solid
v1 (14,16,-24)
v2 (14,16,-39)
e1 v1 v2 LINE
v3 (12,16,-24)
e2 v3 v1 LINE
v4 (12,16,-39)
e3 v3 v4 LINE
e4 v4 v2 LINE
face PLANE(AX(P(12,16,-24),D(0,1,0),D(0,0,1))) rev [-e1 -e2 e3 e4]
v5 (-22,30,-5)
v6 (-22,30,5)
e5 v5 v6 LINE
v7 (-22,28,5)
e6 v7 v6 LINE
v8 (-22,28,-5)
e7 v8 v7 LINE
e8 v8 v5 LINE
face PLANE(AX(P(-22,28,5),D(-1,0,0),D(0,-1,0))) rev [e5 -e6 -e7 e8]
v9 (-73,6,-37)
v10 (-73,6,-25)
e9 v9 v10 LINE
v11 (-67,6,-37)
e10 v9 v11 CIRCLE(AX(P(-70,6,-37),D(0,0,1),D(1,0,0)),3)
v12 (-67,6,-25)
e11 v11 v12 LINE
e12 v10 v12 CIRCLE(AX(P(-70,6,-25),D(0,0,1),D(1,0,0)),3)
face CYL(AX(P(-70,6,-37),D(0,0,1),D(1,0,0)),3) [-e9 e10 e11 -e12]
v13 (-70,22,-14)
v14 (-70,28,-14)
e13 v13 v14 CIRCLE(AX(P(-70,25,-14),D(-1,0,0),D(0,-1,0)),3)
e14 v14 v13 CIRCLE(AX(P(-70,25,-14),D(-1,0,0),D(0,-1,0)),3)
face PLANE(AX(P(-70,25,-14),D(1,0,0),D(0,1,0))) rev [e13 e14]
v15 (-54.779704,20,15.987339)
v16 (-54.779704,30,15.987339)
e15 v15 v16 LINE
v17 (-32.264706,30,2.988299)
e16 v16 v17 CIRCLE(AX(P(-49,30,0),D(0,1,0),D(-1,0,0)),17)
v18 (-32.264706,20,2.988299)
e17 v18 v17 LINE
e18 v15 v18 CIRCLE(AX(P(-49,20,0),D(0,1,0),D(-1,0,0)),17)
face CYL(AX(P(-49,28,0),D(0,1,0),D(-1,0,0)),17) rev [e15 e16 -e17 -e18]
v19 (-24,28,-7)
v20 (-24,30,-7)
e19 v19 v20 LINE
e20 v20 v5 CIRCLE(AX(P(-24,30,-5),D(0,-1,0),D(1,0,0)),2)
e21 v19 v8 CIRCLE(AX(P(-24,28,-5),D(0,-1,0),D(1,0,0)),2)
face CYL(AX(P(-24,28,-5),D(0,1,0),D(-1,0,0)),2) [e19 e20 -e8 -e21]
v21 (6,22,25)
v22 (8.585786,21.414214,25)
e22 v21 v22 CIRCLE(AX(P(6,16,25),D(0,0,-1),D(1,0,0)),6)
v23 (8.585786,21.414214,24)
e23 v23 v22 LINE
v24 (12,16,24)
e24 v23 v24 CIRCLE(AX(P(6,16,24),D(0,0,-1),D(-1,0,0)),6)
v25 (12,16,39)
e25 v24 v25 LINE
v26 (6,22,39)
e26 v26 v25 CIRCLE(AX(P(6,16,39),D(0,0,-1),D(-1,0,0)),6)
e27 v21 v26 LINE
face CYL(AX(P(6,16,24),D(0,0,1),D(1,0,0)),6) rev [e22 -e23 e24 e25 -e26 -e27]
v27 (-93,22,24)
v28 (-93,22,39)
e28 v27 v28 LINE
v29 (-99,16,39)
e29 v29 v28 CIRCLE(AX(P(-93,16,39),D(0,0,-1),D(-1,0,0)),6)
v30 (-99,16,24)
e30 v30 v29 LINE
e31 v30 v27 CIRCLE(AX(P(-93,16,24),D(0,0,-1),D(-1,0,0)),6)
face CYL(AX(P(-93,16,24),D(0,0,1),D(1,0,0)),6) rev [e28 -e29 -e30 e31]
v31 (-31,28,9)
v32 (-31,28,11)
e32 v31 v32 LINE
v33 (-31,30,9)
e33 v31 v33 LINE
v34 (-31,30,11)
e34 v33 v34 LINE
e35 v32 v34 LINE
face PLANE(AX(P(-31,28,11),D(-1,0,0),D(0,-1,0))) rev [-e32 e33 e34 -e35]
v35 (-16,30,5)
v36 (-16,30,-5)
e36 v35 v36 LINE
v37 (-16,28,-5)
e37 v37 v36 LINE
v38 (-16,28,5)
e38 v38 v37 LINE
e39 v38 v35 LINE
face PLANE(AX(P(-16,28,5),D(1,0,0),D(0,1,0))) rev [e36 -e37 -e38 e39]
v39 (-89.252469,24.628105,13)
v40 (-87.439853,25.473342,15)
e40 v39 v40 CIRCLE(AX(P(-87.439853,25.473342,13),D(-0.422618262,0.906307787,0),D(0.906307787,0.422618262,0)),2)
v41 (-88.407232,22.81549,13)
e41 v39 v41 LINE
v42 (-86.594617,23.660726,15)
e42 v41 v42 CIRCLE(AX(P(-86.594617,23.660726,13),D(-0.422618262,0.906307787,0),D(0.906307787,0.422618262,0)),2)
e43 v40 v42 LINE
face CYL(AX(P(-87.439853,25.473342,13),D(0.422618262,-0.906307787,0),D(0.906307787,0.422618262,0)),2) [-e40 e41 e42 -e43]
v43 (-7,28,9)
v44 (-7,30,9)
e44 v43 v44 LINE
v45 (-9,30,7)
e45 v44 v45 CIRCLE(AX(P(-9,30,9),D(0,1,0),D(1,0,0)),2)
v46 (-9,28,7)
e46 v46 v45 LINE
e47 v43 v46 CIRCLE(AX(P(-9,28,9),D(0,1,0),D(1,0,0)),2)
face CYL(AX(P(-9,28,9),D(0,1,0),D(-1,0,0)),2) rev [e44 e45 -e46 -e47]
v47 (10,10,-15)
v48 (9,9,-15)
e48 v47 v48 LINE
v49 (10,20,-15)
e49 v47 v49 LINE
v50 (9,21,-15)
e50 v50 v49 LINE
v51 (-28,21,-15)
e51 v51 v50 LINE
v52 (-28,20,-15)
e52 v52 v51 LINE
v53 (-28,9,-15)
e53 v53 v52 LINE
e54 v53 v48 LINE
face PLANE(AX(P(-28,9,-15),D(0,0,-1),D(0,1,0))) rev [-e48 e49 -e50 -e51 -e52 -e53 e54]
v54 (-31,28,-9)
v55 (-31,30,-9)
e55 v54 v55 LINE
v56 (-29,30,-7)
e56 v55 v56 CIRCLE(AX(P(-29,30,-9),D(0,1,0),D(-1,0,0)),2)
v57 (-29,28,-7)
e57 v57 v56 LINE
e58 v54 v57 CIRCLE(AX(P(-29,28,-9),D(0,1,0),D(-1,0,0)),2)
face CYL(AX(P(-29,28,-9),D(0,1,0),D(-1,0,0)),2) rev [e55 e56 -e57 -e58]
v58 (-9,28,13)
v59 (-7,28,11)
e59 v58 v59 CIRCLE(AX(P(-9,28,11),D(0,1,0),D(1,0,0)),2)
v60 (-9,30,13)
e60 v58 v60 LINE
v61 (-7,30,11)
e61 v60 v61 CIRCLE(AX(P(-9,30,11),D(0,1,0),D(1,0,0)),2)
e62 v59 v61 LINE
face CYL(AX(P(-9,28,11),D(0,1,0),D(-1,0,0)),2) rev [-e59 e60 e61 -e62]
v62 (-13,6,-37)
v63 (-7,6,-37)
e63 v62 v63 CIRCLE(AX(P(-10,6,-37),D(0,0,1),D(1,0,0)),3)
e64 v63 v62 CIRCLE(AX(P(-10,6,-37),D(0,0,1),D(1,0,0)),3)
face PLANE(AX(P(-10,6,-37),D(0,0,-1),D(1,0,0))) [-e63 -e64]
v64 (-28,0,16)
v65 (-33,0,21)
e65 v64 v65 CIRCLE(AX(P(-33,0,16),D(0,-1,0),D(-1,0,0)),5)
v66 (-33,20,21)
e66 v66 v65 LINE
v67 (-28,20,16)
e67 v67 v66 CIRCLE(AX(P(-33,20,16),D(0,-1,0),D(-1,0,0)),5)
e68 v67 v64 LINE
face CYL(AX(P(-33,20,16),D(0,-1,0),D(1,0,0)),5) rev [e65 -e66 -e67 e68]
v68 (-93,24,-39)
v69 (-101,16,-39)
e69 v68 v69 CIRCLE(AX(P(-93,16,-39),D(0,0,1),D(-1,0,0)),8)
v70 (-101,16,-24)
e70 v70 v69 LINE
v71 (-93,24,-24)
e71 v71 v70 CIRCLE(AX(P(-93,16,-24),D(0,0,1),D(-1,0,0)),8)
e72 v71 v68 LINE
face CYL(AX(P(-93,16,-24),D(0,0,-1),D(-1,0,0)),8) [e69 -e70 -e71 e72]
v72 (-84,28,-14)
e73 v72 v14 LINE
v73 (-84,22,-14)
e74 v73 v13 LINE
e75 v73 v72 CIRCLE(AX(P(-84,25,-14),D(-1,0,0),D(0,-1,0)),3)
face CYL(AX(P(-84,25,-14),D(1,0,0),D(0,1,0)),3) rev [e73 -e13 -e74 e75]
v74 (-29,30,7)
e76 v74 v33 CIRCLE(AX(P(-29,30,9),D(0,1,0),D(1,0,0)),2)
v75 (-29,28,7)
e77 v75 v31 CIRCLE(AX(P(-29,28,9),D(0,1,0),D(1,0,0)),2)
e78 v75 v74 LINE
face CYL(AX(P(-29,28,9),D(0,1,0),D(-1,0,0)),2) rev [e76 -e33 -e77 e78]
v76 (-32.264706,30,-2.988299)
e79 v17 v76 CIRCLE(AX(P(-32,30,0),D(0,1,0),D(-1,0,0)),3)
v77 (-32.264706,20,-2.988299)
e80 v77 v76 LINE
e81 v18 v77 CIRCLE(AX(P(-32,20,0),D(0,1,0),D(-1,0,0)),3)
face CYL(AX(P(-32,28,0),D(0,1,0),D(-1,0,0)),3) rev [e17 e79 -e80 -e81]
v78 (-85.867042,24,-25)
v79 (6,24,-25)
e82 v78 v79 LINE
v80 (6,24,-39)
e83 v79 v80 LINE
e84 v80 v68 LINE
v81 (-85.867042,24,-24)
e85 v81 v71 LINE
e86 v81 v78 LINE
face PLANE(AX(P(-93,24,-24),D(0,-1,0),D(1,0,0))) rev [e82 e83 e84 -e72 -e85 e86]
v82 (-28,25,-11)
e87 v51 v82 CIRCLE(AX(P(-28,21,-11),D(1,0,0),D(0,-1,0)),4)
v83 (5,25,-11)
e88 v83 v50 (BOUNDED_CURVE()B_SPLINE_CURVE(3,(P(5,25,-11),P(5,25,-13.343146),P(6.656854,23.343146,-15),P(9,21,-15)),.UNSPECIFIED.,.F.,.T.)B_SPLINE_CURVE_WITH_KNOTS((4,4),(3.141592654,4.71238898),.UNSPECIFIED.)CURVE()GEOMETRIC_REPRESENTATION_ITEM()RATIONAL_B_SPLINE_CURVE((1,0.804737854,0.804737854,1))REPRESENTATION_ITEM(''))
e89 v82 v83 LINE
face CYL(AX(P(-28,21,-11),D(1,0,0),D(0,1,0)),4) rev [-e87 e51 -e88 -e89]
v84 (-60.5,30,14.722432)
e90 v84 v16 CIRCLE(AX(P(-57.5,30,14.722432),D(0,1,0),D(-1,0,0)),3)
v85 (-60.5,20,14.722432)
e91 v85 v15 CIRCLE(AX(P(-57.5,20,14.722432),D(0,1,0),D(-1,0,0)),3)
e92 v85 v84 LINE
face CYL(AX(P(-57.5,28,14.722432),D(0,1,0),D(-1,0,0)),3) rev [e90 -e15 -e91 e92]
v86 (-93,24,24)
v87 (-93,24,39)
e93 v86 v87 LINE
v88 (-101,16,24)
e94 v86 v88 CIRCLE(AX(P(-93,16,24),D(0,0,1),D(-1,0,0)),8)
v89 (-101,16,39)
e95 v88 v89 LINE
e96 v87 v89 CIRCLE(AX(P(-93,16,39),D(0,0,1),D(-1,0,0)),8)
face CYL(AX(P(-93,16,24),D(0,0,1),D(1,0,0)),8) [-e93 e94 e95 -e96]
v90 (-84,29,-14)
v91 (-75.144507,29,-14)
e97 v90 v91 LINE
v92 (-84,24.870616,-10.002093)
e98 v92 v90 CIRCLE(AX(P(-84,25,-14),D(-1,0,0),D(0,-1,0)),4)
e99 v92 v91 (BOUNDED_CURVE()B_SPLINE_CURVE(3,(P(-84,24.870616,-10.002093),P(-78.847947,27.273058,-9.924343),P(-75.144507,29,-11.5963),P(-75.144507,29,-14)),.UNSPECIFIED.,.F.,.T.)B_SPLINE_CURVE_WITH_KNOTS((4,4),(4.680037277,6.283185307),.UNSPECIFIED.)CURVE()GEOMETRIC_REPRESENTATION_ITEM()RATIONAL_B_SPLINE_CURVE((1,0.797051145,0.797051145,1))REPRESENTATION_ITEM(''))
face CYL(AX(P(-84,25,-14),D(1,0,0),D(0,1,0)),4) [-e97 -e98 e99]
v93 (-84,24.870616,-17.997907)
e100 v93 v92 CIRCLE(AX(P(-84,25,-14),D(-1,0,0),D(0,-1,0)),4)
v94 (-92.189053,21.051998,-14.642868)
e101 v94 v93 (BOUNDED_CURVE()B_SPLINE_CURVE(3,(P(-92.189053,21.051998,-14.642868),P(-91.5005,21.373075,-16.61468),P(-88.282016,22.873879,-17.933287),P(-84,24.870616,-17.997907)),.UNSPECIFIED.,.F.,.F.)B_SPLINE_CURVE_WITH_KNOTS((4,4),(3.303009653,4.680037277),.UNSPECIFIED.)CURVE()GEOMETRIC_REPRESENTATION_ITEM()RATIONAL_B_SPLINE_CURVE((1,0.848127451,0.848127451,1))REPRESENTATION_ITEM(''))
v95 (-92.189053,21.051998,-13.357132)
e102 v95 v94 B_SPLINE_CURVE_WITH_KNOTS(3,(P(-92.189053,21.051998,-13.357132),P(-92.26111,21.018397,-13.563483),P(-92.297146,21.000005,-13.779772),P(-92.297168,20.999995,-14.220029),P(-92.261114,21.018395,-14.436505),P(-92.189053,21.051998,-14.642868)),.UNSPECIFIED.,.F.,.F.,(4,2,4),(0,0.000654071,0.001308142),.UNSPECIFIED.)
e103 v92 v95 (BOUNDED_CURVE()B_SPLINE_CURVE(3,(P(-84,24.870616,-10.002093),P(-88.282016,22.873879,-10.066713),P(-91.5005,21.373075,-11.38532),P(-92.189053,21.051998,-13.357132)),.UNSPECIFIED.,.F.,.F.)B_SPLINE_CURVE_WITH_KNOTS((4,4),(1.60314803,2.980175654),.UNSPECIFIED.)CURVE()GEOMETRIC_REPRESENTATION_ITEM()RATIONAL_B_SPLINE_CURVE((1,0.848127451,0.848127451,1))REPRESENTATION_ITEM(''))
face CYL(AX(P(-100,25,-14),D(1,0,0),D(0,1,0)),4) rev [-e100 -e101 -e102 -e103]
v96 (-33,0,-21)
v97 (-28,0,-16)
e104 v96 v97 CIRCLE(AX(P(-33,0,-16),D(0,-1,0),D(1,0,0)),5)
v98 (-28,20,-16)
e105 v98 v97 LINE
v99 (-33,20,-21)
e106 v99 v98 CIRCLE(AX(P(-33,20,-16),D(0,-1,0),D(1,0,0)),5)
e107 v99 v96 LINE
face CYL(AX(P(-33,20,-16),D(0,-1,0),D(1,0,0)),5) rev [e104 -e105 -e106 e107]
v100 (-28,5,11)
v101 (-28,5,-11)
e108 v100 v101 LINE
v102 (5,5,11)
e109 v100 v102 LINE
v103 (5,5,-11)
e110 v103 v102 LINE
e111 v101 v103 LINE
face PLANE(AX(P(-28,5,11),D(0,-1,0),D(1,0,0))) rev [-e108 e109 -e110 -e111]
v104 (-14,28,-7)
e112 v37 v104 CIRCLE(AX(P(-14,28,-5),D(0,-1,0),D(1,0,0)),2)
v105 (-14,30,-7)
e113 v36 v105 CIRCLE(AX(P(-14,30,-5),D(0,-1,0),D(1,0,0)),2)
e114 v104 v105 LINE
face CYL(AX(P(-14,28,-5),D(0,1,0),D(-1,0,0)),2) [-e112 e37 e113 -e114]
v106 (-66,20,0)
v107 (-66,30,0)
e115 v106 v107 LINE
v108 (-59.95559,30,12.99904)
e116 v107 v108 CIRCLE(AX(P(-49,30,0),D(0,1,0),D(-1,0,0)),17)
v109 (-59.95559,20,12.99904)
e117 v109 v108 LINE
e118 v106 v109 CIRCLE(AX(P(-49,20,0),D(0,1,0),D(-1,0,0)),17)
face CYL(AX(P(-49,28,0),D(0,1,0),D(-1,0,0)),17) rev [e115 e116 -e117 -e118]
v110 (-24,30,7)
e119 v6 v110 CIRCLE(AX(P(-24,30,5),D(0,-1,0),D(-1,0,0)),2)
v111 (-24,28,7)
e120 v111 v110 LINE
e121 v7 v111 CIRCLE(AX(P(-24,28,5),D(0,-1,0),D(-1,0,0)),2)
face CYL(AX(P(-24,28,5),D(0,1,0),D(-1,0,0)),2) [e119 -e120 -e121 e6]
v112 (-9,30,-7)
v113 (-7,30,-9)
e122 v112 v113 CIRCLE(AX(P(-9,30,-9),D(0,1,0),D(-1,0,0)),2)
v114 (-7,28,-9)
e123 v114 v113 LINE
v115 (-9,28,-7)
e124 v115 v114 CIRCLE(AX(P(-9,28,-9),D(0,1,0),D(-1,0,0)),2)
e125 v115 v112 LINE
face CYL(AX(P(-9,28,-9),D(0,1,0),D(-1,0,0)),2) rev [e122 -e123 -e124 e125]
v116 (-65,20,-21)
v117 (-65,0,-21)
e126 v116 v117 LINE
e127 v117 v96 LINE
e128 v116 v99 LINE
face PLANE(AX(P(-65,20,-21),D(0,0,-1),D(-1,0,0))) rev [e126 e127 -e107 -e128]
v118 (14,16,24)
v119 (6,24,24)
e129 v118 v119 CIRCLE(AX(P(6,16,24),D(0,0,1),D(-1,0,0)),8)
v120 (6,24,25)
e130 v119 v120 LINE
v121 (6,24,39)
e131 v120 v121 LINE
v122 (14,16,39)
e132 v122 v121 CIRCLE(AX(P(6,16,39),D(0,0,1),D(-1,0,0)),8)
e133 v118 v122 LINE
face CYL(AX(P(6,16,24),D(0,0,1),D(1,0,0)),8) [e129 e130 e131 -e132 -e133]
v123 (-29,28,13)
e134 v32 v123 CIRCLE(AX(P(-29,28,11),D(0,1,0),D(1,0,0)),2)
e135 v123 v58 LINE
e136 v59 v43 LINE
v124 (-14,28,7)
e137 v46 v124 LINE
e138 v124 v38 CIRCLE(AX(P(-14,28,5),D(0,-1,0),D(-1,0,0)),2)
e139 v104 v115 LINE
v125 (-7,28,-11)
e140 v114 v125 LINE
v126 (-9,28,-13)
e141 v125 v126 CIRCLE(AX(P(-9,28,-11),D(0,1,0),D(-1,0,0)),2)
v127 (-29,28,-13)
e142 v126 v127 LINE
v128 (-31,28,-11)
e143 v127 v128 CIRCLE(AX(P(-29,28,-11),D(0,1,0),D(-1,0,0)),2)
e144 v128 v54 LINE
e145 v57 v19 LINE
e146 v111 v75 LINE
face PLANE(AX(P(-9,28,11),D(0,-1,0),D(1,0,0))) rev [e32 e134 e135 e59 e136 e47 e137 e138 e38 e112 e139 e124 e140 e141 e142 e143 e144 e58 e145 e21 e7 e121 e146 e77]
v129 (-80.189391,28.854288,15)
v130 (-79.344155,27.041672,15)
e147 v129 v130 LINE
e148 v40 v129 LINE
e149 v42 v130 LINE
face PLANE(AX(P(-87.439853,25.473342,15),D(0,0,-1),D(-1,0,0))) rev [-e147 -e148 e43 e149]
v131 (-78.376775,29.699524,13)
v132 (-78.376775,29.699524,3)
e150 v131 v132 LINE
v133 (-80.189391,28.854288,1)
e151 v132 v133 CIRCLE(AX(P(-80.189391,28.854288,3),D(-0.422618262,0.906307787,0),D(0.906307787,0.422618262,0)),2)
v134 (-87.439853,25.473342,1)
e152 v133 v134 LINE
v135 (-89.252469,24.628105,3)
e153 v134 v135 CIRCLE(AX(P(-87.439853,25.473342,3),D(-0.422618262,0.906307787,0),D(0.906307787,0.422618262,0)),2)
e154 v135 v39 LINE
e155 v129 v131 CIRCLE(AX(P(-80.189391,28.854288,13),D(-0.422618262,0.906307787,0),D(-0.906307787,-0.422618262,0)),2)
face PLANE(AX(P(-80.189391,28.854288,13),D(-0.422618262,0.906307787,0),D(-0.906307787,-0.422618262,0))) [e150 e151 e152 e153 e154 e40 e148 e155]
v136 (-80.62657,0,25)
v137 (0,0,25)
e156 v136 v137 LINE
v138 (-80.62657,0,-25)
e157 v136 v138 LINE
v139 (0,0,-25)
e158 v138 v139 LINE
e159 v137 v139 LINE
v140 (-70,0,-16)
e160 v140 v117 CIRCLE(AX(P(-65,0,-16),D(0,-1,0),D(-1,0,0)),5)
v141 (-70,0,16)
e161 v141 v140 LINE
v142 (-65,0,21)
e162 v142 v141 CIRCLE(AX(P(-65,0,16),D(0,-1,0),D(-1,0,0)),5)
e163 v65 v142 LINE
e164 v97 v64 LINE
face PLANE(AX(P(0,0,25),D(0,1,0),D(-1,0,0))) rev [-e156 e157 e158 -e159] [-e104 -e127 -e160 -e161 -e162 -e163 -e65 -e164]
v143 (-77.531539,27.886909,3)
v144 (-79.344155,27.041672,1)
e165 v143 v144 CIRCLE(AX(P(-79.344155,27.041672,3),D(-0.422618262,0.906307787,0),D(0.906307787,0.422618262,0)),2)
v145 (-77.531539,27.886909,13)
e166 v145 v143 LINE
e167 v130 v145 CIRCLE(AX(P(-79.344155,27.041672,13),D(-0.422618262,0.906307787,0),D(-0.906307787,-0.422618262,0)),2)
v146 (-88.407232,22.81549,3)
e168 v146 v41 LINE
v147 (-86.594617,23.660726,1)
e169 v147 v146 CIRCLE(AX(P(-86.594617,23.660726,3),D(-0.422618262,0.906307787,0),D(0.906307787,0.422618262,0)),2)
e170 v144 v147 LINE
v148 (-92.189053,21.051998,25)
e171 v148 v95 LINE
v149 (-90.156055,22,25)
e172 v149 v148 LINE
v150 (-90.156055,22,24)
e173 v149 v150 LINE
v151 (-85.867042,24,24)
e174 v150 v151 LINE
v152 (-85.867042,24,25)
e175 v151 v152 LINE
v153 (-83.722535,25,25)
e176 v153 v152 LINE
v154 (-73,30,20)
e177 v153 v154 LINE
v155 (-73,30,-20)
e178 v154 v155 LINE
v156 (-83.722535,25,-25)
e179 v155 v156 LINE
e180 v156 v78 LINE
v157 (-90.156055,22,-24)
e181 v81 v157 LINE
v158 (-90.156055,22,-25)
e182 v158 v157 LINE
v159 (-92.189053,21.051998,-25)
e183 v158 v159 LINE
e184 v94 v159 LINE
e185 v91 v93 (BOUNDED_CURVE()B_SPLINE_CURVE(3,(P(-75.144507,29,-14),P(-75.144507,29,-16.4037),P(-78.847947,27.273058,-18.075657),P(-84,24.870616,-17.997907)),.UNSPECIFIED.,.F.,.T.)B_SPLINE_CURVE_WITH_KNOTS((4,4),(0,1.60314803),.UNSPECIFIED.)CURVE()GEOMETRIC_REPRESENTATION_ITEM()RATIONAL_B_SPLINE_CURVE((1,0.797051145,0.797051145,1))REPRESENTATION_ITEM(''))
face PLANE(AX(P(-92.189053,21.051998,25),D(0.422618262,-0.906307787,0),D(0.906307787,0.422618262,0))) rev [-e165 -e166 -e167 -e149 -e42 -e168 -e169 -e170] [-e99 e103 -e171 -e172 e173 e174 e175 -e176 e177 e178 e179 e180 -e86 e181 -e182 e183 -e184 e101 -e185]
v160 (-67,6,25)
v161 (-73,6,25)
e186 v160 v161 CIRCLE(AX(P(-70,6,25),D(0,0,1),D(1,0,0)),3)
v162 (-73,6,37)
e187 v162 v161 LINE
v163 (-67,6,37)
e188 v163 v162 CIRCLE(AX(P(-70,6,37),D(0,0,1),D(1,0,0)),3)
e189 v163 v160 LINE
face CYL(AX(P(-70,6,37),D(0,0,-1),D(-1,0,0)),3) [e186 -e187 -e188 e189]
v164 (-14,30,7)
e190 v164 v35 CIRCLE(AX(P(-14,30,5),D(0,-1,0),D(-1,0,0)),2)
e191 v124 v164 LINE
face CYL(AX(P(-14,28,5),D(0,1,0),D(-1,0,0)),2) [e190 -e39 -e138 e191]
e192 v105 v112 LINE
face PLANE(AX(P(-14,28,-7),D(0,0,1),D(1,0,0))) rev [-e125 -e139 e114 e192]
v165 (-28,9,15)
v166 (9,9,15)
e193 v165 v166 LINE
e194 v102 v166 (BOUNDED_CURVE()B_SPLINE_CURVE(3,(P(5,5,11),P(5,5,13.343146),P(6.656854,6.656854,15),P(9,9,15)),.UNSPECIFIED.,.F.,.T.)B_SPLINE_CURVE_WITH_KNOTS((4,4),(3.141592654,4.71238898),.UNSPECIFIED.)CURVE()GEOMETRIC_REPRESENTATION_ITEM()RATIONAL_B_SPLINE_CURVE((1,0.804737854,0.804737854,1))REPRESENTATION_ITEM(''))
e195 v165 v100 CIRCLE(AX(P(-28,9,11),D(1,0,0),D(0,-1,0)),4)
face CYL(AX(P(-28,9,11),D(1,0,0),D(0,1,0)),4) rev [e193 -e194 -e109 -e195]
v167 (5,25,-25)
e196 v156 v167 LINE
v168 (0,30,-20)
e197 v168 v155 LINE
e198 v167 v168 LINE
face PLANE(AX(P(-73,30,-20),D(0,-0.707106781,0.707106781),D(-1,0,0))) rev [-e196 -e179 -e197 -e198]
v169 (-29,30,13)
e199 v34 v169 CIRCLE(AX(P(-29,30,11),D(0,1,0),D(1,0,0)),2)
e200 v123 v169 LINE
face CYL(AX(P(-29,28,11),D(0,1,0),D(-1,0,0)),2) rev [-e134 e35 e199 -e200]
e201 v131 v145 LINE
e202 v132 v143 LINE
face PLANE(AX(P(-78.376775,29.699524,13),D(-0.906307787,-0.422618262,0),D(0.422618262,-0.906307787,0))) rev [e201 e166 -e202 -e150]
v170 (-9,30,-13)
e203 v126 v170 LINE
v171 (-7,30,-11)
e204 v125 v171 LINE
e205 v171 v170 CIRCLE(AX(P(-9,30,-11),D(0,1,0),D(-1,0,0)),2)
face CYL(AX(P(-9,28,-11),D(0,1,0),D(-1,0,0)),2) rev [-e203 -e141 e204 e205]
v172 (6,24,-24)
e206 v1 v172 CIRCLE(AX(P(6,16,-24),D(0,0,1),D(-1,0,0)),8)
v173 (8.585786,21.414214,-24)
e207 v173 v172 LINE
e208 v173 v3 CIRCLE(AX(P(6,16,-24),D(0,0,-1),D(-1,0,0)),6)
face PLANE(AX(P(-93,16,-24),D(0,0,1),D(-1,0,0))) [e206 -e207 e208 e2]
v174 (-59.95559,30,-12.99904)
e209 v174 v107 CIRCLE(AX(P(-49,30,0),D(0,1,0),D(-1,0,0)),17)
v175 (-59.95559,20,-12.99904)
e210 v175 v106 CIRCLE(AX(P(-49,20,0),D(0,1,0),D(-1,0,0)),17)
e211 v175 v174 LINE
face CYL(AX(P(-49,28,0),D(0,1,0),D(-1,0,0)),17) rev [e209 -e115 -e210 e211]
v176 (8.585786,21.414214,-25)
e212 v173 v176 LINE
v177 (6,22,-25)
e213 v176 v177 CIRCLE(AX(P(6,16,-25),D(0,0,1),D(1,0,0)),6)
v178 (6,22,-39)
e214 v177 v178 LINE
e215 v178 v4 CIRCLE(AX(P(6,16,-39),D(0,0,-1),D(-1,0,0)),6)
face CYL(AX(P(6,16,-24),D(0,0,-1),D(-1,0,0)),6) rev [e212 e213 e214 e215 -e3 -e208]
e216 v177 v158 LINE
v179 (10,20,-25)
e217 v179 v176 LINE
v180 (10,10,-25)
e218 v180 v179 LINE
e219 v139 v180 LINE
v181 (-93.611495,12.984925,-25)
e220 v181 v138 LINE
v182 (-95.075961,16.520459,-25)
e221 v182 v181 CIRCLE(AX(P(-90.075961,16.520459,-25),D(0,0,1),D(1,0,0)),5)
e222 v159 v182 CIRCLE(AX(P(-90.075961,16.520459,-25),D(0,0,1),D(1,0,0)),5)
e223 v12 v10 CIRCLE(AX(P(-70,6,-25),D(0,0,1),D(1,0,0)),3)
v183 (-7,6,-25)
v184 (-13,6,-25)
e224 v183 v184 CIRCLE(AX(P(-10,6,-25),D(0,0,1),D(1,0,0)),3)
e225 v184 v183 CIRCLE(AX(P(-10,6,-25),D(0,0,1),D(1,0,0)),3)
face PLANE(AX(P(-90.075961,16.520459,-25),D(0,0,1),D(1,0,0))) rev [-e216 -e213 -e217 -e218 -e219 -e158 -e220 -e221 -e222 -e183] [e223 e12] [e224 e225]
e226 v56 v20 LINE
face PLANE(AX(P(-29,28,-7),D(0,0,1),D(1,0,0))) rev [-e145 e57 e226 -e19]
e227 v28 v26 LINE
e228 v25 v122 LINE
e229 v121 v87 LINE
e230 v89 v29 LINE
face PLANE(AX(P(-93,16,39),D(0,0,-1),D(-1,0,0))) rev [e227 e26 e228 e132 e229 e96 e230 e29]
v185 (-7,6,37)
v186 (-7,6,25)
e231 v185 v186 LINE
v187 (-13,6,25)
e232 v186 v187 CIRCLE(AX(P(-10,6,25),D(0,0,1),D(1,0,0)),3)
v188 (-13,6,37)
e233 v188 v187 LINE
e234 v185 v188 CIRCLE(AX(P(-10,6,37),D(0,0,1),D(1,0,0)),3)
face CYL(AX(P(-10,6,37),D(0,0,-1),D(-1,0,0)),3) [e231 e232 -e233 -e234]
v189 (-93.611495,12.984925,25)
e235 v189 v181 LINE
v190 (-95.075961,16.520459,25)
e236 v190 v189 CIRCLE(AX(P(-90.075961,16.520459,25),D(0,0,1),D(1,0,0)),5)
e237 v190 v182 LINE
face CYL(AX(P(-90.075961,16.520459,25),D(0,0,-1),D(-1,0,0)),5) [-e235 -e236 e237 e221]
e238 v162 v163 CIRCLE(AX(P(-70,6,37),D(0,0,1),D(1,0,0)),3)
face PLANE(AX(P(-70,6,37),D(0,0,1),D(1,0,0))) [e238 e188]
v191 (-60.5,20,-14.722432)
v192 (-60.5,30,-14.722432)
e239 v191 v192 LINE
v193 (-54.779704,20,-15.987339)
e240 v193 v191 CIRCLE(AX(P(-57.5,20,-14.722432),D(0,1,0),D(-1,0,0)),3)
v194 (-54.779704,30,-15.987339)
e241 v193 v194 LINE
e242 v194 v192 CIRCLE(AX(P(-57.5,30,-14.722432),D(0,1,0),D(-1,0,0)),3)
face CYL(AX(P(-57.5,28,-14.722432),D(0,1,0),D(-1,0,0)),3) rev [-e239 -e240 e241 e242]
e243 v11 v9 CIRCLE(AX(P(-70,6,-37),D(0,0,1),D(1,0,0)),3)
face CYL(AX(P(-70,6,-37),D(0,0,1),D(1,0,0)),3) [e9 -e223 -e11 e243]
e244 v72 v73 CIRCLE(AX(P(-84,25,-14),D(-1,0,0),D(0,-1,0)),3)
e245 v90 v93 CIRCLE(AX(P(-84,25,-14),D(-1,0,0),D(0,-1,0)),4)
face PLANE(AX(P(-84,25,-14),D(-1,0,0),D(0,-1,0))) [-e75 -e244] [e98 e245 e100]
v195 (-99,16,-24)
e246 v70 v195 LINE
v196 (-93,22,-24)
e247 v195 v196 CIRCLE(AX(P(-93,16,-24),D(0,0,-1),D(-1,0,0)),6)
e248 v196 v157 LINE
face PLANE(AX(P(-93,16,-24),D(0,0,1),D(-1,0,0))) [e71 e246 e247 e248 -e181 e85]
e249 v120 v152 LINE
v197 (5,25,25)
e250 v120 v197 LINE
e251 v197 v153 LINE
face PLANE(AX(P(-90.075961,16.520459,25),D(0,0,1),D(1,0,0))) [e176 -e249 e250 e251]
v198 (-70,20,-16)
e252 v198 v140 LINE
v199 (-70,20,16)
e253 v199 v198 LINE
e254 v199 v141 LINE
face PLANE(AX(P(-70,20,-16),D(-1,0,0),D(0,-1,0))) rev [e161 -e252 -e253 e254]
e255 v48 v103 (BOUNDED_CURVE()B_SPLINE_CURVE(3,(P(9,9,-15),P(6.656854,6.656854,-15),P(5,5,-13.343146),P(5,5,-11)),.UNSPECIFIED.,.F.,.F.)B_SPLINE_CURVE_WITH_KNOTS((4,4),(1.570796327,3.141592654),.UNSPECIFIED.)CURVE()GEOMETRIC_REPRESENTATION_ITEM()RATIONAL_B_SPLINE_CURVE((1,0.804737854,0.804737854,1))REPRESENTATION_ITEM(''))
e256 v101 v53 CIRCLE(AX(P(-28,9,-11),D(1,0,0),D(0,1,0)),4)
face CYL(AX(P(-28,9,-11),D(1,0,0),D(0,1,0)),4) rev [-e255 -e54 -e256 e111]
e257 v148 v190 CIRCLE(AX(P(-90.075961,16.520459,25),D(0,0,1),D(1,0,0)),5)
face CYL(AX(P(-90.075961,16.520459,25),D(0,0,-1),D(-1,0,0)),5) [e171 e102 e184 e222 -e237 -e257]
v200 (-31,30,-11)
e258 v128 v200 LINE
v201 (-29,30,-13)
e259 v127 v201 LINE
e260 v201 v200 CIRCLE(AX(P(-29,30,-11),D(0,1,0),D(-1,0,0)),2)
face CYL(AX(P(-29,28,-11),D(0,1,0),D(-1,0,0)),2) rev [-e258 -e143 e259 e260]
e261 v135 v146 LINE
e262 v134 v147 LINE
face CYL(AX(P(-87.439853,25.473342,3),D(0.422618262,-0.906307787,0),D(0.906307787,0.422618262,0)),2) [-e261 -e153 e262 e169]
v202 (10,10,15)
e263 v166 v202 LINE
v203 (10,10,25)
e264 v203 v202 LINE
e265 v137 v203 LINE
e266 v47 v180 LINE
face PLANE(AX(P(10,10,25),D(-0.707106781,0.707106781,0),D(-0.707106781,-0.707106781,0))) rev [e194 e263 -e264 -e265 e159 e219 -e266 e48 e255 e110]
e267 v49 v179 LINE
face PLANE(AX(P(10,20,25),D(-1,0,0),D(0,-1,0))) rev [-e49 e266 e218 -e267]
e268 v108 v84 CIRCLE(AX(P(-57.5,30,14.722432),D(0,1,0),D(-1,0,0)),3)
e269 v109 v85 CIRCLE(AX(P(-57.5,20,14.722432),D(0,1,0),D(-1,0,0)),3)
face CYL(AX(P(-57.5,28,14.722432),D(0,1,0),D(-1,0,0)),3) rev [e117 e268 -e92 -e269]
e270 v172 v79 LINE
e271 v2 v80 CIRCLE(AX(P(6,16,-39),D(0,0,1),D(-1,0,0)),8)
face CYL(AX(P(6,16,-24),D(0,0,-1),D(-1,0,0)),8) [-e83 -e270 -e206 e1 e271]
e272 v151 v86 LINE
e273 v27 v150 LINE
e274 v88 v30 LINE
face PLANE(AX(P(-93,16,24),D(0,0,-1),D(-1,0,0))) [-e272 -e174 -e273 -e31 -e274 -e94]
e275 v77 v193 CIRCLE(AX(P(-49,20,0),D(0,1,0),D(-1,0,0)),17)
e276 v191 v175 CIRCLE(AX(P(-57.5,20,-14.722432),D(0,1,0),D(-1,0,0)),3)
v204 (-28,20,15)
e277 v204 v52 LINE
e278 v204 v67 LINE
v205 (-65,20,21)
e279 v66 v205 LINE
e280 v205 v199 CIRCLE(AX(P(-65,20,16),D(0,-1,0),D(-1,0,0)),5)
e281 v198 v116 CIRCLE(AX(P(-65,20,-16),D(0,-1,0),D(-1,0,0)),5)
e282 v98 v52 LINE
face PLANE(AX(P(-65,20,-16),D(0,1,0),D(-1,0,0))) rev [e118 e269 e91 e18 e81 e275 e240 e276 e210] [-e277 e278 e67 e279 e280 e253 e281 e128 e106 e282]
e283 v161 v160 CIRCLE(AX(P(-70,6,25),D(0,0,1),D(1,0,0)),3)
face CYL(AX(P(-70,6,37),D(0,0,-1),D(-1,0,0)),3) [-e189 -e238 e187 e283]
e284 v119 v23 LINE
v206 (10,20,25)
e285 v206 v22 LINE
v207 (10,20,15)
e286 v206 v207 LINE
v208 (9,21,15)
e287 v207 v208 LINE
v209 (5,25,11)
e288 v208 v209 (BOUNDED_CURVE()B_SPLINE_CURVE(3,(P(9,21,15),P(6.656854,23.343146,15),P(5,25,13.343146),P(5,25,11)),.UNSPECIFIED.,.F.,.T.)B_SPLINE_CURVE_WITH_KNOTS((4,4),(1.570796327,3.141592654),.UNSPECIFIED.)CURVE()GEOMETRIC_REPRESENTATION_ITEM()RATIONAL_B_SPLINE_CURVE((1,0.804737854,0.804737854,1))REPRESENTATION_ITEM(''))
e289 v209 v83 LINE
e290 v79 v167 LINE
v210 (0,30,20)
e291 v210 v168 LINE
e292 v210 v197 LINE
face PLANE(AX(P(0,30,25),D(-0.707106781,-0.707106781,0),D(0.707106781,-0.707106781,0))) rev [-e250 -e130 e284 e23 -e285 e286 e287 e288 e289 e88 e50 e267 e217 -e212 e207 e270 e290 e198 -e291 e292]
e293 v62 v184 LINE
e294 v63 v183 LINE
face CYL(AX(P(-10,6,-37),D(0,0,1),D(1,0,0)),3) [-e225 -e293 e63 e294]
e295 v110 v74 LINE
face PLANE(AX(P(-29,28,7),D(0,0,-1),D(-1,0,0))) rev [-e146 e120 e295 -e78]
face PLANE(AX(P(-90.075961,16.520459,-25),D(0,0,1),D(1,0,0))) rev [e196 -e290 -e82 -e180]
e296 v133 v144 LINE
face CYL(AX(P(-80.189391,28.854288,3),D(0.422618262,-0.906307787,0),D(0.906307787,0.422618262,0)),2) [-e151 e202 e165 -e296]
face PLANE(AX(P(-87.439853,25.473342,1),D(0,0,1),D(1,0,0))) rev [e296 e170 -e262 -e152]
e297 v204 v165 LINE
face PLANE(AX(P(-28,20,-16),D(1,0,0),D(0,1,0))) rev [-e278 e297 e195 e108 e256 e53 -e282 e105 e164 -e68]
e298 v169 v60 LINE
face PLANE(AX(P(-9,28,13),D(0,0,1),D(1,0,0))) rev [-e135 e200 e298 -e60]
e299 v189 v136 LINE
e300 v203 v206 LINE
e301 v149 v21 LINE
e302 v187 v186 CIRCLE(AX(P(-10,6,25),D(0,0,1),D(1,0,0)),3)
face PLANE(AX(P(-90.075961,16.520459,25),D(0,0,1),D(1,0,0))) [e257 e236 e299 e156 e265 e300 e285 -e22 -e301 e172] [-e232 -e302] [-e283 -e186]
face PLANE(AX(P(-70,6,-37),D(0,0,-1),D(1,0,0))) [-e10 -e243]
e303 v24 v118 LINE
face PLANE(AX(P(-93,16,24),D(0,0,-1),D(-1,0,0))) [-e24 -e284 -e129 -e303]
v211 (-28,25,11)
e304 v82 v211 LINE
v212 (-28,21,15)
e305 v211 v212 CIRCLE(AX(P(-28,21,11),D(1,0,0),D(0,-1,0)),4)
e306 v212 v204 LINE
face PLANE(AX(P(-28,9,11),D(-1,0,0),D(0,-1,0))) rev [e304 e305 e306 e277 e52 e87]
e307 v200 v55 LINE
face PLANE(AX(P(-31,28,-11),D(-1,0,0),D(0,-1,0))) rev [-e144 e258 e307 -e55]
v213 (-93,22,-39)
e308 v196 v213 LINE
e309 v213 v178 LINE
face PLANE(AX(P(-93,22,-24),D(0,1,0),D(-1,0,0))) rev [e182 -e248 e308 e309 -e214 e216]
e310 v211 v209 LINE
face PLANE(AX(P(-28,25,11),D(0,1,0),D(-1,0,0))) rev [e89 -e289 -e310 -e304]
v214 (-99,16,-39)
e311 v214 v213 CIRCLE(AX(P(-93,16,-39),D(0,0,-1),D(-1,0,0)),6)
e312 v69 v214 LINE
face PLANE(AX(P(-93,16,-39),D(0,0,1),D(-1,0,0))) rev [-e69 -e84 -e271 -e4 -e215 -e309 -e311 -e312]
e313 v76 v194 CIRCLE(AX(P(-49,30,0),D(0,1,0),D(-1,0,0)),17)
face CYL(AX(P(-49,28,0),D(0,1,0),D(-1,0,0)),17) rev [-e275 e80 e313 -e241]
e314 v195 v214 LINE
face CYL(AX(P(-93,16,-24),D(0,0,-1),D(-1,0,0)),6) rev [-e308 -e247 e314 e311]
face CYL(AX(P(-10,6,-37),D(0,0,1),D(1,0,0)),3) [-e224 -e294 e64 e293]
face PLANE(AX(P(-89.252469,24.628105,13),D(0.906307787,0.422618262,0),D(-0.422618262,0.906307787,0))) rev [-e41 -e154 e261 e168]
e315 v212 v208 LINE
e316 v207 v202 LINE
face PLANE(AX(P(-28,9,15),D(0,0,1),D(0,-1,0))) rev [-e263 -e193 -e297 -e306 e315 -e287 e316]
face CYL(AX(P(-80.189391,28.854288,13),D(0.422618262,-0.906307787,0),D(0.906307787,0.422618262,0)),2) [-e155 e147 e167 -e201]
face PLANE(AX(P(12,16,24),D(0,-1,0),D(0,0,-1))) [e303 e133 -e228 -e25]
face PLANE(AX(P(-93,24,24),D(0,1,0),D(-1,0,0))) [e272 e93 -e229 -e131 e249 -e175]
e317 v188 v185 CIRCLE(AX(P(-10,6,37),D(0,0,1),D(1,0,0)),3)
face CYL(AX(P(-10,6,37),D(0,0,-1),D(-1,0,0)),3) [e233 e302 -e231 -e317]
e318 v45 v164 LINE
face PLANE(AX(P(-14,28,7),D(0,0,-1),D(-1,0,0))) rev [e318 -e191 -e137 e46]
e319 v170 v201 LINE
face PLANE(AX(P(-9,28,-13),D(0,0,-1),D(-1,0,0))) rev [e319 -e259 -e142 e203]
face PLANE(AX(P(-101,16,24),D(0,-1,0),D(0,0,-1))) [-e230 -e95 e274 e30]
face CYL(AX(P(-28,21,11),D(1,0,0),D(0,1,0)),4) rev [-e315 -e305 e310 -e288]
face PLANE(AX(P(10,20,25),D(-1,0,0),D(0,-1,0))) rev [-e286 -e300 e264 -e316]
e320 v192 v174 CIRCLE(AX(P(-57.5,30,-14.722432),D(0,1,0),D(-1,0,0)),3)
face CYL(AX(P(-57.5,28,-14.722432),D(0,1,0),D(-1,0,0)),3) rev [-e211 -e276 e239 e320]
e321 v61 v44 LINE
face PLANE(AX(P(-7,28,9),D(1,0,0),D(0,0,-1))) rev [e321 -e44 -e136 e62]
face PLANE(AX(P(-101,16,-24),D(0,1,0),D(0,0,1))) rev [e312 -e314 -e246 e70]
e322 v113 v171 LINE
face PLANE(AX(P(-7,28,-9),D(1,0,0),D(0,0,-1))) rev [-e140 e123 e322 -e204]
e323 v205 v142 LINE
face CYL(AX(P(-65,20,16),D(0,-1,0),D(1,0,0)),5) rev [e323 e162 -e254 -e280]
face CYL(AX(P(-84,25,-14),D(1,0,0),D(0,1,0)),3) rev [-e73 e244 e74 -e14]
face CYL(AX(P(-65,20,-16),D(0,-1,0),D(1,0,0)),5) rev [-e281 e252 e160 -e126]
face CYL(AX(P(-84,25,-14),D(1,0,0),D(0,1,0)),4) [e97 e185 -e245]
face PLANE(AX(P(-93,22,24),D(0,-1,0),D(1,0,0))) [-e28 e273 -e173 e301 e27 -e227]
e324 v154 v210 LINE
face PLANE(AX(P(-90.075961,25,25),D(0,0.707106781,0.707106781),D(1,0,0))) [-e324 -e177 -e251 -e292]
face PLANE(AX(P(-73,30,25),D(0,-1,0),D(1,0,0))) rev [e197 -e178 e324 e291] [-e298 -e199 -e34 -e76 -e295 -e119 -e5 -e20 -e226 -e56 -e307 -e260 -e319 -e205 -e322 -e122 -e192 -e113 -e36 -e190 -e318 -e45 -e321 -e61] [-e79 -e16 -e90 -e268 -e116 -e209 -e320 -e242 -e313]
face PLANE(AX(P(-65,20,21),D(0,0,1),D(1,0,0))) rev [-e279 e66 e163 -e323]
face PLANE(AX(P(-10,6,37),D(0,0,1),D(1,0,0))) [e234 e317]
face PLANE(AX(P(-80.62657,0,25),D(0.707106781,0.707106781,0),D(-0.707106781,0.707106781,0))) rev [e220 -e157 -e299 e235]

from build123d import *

# Parameters (mm, degrees)
BOSS_EXTRUDE1_DEPTH = 25
CHAMFER1_SIZE       = 5
BOSS_EXTRUDE2_DEPTH = 2
CUT_EXTRUDE1_DEPTH  = 2
CUT_EXTRUDE2_DEPTH  = 8
CUT_EXTRUDE3_DEPTH  = 38
CUT_EXTRUDE4_DEPTH  = 20
CUT_EXTRUDE6_START  = -80
SKETCH7_R           = 4
CUT_EXTRUDE6_DEPTH  = 30
BOSS_EXTRUDE3_START = -1
BOSS_EXTRUDE3_DEPTH = 15
SKETCH9_R           = 3
BOSS_EXTRUDE4_DEPTH = 12
SKETCH10_R          = 4
SKETCH10_R_2        = 3
BOSS_EXTRUDE5_DEPTH = 14


with BuildPart() as part:
    # Sketch1 → Boss-Extrude1 (new, symmetric)
    with BuildSketch(Plane.XY):
        with BuildLine():
            Line((0, 0), (-80.626570136, 0))
            Line((-80.626570136, 0), (-93.611495141, 12.984925005))
            ThreePointArc((-93.611495141, 12.984925005), (-95, 17.388699799), (-92.189052544, 21.051997846))
            Line((-92.189052544, 21.051997846), (-73, 30))
            Line((-73, 30), (0, 30))
            Line((0, 30), (10, 20))
            Line((10, 20), (10, 10))
            Line((10, 10), (0, 0))
        make_face()
    extrude(amount=BOSS_EXTRUDE1_DEPTH, both=True)

    # Chamfer1
    chamfer1_edges = [part.edges().sort_by_distance(p)[0] for p in [
        (-36.5, 30, -25),
        (-36.5, 30, 25),
    ]]
    chamfer(chamfer1_edges, length=CHAMFER1_SIZE)

    # Sketch3 → Boss-Extrude2 (add)
    with BuildSketch(Plane(origin=(-24.528918893, 52.602436319, 0), x_dir=(0.9063077870366526, 0.4226182617406939, 0), z_dir=(-0.4226182617406939, 0.9063077870366526, 0))):
        with BuildLine():
            Line((-68.481920601, -15), (-60.481920601, -15))
            ThreePointArc((-60.481920601, -15), (-59.067707039, -14.414213562), (-58.481920601, -13))
            Line((-58.481920601, -13), (-58.481920601, -3))
            ThreePointArc((-58.481920601, -3), (-59.067707039, -1.585786438), (-60.481920601, -1))
            Line((-60.481920601, -1), (-68.481920601, -1))
            ThreePointArc((-68.481920601, -1), (-69.896134164, -1.585786438), (-70.481920601, -3))
            Line((-70.481920601, -3), (-70.481920601, -13))
            ThreePointArc((-70.481920601, -13), (-69.896134164, -14.414213562), (-68.481920601, -15))
        make_face()
    extrude(amount=BOSS_EXTRUDE2_DEPTH)

    # Sketch2 → Cut-Extrude1 (cut)
    with BuildSketch(Plane(origin=(0, 30, 0), x_dir=(1, 0, 0), z_dir=(0, 1, 0))):
        with BuildLine():
            Line((-14, -7), (-9, -7))
            ThreePointArc((-9, -7), (-7.585786438, -7.585786438), (-7, -9))
            Line((-7, -9), (-7, -11))
            ThreePointArc((-7, -11), (-7.585786438, -12.414213562), (-9, -13))
            Line((-9, -13), (-29, -13))
            ThreePointArc((-29, -13), (-30.414213562, -12.414213562), (-31, -11))
            Line((-31, -11), (-31, -9))
            ThreePointArc((-31, -9), (-30.414213562, -7.585786438), (-29, -7))
            Line((-29, -7), (-24, -7))
            ThreePointArc((-24, -7), (-22.585786438, -6.414213562), (-22, -5))
            Line((-22, -5), (-22, 5))
            ThreePointArc((-22, 5), (-22.585786438, 6.414213562), (-24, 7))
            Line((-24, 7), (-29, 7))
            ThreePointArc((-29, 7), (-30.414213562, 7.585786438), (-31, 9))
            Line((-31, 9), (-31, 11))
            ThreePointArc((-31, 11), (-30.414213562, 12.414213562), (-29, 13))
            Line((-29, 13), (-9, 13))
            ThreePointArc((-9, 13), (-7.585786438, 12.414213562), (-7, 11))
            Line((-7, 11), (-7, 9))
            ThreePointArc((-7, 9), (-7.585786438, 7.585786438), (-9, 7))
            Line((-9, 7), (-14, 7))
            ThreePointArc((-14, 7), (-15.414213562, 6.414213562), (-16, 5))
            Line((-16, 5), (-16, -5))
            ThreePointArc((-16, -5), (-15.414213562, -6.414213562), (-14, -7))
        make_face()
        with BuildLine():
            ThreePointArc((-59.95558989, 12.999040356), (-66, 0), (-59.95558989, -12.999040356))
            ThreePointArc((-59.95558989, -12.999040356), (-59, -17.320508076), (-54.779704228, -15.987339336))
            ThreePointArc((-54.779704228, -15.987339336), (-40.5, -14.722431864), (-32.264705882, -2.98829898))
            ThreePointArc((-32.264705882, -2.98829898), (-29, 0), (-32.264705882, 2.98829898))
            ThreePointArc((-32.264705882, 2.98829898), (-40.5, 14.722431864), (-54.779704228, 15.987339336))
            ThreePointArc((-54.779704228, 15.987339336), (-59, 17.320508076), (-59.95558989, 12.999040356))
        make_face()
    extrude(amount=-CUT_EXTRUDE1_DEPTH, mode=Mode.SUBTRACT)

    # Sketch4 → Cut-Extrude2 (cut)
    with BuildSketch(Plane(origin=(0, 28, 0), x_dir=(1, 0, 0), z_dir=(0, 1, 0))):
        with BuildLine():
            ThreePointArc((-54.779704228, -15.987339336), (-40.5, -14.722431864), (-32.264705882, -2.98829898))
            ThreePointArc((-32.264705882, -2.98829898), (-29, 0), (-32.264705882, 2.98829898))
            ThreePointArc((-32.264705882, 2.98829898), (-40.5, 14.722431864), (-54.779704228, 15.987339336))
            ThreePointArc((-54.779704228, 15.987339336), (-59, 17.320508076), (-59.95558989, 12.999040356))
            ThreePointArc((-59.95558989, 12.999040356), (-66, 0), (-59.95558989, -12.999040356))
            ThreePointArc((-59.95558989, -12.999040356), (-59, -17.320508076), (-54.779704228, -15.987339336))
        make_face()
    extrude(amount=-CUT_EXTRUDE2_DEPTH, mode=Mode.SUBTRACT)

    # Sketch5 → Cut-Extrude3 (cut)
    with BuildSketch(Plane(origin=(10, 0, 0), x_dir=(0, 0, -1), z_dir=(1, 0, 0))):
        with BuildLine():
            Line((-11, 5), (11, 5))
            ThreePointArc((11, 5), (13.828427125, 6.171572875), (15, 9))
            Line((15, 9), (15, 21))
            ThreePointArc((15, 21), (13.828427125, 23.828427125), (11, 25))
            Line((11, 25), (-11, 25))
            ThreePointArc((-11, 25), (-13.828427125, 23.828427125), (-15, 21))
            Line((-15, 21), (-15, 9))
            ThreePointArc((-15, 9), (-13.828427125, 6.171572875), (-11, 5))
        make_face()
    extrude(amount=-CUT_EXTRUDE3_DEPTH, mode=Mode.SUBTRACT)

    # Sketch6 → Cut-Extrude4 (cut)
    with BuildSketch(Plane.XZ):
        with BuildLine():
            Line((-65, -21), (-33, -21))
            ThreePointArc((-33, -21), (-29.464466094, -19.535533906), (-28, -16))
            Line((-28, -16), (-28, 16))
            ThreePointArc((-28, 16), (-29.464466094, 19.535533906), (-33, 21))
            Line((-33, 21), (-65, 21))
            ThreePointArc((-65, 21), (-68.535533906, 19.535533906), (-70, 16))
            Line((-70, 16), (-70, -16))
            ThreePointArc((-70, -16), (-68.535533906, -19.535533906), (-65, -21))
        make_face()
    extrude(amount=-CUT_EXTRUDE4_DEPTH, mode=Mode.SUBTRACT)

    # Sketch7 → Cut-Extrude6 (cut)
    with BuildSketch(Plane(origin=(10, 0, 0), x_dir=(0, 0, -1), z_dir=(1, 0, 0)).offset(CUT_EXTRUDE6_START)):
        with Locations(Location((14, 25, 0), (0, 0, 90))):
            Circle(SKETCH7_R)
    extrude(amount=-CUT_EXTRUDE6_DEPTH, mode=Mode.SUBTRACT)

    # Sketch8 → Boss-Extrude3 (add)
    with BuildSketch(Plane.XY.offset(25).offset(BOSS_EXTRUDE3_START)):
        with BuildLine():
            Line((-93, 24), (6, 24))
            ThreePointArc((6, 24), (11.656854249, 21.656854249), (14, 16))
            Line((14, 16), (12, 16))
            ThreePointArc((12, 16), (10.242640687, 20.242640687), (6, 22))
            Line((6, 22), (-93, 22))
            ThreePointArc((-93, 22), (-97.242640687, 20.242640687), (-99, 16))
            Line((-99, 16), (-101, 16))
            ThreePointArc((-101, 16), (-98.656854249, 21.656854249), (-93, 24))
        make_face()
    boss_extrude3 = extrude(amount=BOSS_EXTRUDE3_DEPTH)

    # Sketch9 → Boss-Extrude4 (add)
    with BuildSketch(Plane.XY.offset(25)):
        with Locations((-70, 6)):
            Circle(SKETCH9_R)
        with Locations((-10, 6)):
            Circle(SKETCH9_R)
    boss_extrude4 = extrude(amount=BOSS_EXTRUDE4_DEPTH)

    # Mirror1: Boss-Extrude3, Boss-Extrude4 across plane
    add(boss_extrude3.mirror(Plane.XY))
    add(boss_extrude4.mirror(Plane.XY))

    # Sketch10 → Boss-Extrude5 (add)
    with BuildSketch(Plane.ZY.offset(70)):
        with Locations((-14, 25)):
            Circle(SKETCH10_R)
        with Locations(Location((-14, 25, 0), (0, 0, 270))):
            Circle(SKETCH10_R_2, mode=Mode.SUBTRACT)
    extrude(amount=BOSS_EXTRUDE5_DEPTH)


solid = part.part
